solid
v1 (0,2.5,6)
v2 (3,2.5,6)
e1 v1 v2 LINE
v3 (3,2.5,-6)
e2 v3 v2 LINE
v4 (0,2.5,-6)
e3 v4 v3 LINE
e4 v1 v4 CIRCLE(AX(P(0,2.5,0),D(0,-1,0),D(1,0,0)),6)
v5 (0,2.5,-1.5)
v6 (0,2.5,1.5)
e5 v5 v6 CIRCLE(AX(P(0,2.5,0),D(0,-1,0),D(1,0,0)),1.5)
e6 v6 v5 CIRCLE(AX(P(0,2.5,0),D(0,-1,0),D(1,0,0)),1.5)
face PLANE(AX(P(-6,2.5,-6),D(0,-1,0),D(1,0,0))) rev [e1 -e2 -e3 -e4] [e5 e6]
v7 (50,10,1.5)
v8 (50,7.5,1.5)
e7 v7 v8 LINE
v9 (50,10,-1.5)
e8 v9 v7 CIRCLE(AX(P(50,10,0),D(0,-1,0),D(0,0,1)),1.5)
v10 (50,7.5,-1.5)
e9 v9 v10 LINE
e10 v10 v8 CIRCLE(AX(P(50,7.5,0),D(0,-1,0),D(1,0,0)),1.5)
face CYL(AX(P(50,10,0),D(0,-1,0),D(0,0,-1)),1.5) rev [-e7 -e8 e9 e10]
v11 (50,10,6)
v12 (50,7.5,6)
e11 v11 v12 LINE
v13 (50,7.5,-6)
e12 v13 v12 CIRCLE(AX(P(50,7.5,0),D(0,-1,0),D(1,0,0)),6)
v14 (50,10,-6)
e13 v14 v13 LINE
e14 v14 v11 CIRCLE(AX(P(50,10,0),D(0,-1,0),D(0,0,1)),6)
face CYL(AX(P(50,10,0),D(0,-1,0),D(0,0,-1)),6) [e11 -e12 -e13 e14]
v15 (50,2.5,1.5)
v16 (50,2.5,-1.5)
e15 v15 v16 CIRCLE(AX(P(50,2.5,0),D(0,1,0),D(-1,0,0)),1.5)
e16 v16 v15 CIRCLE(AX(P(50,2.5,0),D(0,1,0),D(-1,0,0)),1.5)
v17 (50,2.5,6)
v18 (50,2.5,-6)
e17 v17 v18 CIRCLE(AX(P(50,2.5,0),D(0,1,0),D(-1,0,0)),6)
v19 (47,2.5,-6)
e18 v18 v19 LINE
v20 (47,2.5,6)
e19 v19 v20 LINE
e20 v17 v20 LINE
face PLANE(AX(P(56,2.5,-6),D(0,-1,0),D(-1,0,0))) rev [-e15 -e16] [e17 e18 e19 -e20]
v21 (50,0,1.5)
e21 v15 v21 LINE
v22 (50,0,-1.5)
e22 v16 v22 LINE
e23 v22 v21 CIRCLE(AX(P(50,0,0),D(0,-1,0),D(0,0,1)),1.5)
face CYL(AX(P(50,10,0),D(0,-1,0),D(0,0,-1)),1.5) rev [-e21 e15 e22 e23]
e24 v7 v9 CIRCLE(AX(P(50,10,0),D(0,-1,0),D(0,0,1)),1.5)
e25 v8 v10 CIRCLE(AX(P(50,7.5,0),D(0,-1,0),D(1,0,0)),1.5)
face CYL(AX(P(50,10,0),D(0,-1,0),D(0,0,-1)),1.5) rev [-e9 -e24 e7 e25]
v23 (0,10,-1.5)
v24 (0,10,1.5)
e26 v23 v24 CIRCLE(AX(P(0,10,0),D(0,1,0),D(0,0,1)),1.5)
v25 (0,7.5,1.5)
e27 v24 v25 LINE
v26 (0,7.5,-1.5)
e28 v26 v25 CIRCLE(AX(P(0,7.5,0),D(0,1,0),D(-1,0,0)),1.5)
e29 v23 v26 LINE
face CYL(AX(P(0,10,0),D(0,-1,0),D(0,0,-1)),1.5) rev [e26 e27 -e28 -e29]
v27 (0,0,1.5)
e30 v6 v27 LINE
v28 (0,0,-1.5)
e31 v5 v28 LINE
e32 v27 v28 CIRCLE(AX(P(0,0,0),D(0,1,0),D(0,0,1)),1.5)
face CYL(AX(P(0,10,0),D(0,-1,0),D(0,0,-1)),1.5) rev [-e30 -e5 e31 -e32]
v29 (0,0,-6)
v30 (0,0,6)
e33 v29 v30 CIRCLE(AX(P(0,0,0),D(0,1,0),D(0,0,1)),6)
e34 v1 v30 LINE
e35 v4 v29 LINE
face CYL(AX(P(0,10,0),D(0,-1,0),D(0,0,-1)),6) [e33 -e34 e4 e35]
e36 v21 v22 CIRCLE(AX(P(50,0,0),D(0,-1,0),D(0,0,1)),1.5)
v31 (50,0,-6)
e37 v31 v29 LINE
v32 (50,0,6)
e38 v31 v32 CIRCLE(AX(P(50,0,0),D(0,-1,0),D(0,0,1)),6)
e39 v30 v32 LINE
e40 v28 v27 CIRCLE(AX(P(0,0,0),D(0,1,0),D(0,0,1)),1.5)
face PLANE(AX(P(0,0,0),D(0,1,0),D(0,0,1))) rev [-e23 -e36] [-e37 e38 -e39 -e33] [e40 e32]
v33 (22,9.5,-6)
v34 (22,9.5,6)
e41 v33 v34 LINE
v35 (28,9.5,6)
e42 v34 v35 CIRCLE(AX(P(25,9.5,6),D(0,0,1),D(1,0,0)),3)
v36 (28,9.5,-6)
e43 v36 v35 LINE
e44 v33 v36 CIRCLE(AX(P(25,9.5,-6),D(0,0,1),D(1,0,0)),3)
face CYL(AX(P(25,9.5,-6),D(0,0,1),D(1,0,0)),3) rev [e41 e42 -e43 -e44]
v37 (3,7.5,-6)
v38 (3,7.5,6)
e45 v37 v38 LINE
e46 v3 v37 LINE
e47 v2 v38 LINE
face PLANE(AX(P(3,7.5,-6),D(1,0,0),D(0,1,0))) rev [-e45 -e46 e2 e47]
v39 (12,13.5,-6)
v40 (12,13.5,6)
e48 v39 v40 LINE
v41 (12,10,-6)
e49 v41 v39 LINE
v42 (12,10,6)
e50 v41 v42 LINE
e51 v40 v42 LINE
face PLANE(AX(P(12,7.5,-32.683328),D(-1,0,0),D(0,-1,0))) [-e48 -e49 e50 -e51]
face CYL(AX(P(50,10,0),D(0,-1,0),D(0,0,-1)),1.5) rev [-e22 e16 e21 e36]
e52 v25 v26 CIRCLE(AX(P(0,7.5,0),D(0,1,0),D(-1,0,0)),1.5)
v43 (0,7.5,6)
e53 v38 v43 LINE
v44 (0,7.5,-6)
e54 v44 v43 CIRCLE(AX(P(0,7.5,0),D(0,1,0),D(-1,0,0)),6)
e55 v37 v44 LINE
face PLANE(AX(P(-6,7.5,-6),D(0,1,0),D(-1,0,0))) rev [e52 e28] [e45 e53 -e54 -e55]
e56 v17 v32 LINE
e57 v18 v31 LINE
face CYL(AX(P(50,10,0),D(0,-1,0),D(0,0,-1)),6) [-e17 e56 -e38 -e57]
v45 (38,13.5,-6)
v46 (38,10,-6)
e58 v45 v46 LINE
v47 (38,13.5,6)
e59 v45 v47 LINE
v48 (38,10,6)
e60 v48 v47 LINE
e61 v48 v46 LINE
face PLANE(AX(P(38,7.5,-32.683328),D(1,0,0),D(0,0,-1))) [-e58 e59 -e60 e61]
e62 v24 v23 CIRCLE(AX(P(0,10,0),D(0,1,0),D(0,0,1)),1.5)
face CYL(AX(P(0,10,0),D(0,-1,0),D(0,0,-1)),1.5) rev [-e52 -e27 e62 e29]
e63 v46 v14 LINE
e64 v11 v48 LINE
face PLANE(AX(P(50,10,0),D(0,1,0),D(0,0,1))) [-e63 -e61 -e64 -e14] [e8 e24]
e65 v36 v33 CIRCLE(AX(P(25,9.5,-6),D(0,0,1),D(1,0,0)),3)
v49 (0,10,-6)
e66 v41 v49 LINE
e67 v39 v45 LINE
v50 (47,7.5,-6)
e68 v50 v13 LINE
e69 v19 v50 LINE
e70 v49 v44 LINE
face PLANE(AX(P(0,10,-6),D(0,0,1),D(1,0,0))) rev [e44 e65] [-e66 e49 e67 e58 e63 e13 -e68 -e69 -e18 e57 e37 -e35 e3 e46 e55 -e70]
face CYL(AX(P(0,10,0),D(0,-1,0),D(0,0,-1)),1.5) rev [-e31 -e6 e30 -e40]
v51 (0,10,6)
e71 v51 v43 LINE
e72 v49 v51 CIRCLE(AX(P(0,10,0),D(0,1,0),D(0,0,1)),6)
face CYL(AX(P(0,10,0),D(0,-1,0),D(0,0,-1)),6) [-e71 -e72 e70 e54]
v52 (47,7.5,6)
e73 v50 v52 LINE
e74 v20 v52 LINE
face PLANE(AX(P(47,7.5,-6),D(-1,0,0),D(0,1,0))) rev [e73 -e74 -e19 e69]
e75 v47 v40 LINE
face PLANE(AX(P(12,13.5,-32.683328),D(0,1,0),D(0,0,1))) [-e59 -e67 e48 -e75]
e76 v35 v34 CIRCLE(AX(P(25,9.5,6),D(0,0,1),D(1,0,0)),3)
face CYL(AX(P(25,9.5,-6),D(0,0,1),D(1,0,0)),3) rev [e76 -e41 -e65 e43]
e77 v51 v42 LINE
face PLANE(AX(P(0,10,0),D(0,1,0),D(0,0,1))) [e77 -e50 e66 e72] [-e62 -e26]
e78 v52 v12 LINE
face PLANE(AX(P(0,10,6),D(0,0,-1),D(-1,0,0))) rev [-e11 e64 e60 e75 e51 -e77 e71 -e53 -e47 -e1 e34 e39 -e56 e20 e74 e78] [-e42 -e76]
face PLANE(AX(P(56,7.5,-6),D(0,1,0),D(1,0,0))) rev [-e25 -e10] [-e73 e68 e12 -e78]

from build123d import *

# Parameters (mm, degrees)
SKETCH1_R           = 1.5
BOSS_EXTRUDE1_DEPTH = 10
SKETCH2_W           = 9
SKETCH2_H           = 5
CUT_EXTRUDE1_DEPTH  = 24.832750576
SKETCH3_W           = 12
SKETCH3_H           = 5
BOSS_EXTRUDE2_DEPTH = 32
SKETCH5_W           = 26
SKETCH5_H           = 6
SKETCH5_H_2         = 2.5
BOSS_EXTRUDE6_DEPTH = 12
SKETCH6_R           = 3
CUT_EXTRUDE2_DEPTH  = 59.840887145


with BuildPart() as part:
    # Sketch1 → Boss-Extrude1 (new body)
    with BuildSketch(Plane(origin=(0, 0, 0), x_dir=(1, 0, 0), z_dir=(0, 1, 0))):
        with BuildLine():
            Line((0, 6), (12, 6))
            ThreePointArc((12, 6), (18, 0), (12, -6))
            Line((12, -6), (0, -6))
            ThreePointArc((0, -6), (-6, 0), (0, 6))
        make_face()
        with Locations(Location((0, 0, 0), (0, 0, 270))):
            Circle(SKETCH1_R, mode=Mode.SUBTRACT)
    extrude(amount=BOSS_EXTRUDE1_DEPTH)

    # Sketch2 → Cut-Extrude1 (cut, through all)
    with BuildSketch(Plane.XY.offset(6)):
        with Locations((-1.5, 5)):
            Rectangle(SKETCH2_W, SKETCH2_H)
        with Locations((13.5, 5)):
            Rectangle(SKETCH2_W, SKETCH2_H)
    extrude(amount=-CUT_EXTRUDE1_DEPTH, mode=Mode.SUBTRACT)

    # Sketch3 → Boss-Extrude2 (add)
    with BuildSketch(Plane(origin=(9, 0, 0), x_dir=(0, 0, -1), z_dir=(1, 0, 0))):
        with Locations((0, 5)):
            Rectangle(SKETCH3_W, SKETCH3_H)
    extrude(amount=BOSS_EXTRUDE2_DEPTH)

    # Mirror1: part across plane


with BuildPart() as part_1:
    add(part.part)
    add(part.part.mirror(Plane(origin=(25, 0, 0), x_dir=(0, 0, 1), z_dir=(1, 0, 0))))

    # Sketch5 → Boss-Extrude6 (add)
    with BuildSketch(Plane.XY.offset(6)):
        with Locations((25, 10.5)):
            Rectangle(SKETCH5_W, SKETCH5_H)
        with Locations((25, 1.25)):
            Rectangle(SKETCH5_W, SKETCH5_H_2)
    extrude(amount=-BOSS_EXTRUDE6_DEPTH)

    # Sketch6 → Cut-Extrude2 (cut, through all)
    with BuildSketch(Plane.XY.offset(6)):
        with Locations((25, 9.5)):
            Circle(SKETCH6_R)
    extrude(amount=-CUT_EXTRUDE2_DEPTH, mode=Mode.SUBTRACT)


solid = part_1.part
